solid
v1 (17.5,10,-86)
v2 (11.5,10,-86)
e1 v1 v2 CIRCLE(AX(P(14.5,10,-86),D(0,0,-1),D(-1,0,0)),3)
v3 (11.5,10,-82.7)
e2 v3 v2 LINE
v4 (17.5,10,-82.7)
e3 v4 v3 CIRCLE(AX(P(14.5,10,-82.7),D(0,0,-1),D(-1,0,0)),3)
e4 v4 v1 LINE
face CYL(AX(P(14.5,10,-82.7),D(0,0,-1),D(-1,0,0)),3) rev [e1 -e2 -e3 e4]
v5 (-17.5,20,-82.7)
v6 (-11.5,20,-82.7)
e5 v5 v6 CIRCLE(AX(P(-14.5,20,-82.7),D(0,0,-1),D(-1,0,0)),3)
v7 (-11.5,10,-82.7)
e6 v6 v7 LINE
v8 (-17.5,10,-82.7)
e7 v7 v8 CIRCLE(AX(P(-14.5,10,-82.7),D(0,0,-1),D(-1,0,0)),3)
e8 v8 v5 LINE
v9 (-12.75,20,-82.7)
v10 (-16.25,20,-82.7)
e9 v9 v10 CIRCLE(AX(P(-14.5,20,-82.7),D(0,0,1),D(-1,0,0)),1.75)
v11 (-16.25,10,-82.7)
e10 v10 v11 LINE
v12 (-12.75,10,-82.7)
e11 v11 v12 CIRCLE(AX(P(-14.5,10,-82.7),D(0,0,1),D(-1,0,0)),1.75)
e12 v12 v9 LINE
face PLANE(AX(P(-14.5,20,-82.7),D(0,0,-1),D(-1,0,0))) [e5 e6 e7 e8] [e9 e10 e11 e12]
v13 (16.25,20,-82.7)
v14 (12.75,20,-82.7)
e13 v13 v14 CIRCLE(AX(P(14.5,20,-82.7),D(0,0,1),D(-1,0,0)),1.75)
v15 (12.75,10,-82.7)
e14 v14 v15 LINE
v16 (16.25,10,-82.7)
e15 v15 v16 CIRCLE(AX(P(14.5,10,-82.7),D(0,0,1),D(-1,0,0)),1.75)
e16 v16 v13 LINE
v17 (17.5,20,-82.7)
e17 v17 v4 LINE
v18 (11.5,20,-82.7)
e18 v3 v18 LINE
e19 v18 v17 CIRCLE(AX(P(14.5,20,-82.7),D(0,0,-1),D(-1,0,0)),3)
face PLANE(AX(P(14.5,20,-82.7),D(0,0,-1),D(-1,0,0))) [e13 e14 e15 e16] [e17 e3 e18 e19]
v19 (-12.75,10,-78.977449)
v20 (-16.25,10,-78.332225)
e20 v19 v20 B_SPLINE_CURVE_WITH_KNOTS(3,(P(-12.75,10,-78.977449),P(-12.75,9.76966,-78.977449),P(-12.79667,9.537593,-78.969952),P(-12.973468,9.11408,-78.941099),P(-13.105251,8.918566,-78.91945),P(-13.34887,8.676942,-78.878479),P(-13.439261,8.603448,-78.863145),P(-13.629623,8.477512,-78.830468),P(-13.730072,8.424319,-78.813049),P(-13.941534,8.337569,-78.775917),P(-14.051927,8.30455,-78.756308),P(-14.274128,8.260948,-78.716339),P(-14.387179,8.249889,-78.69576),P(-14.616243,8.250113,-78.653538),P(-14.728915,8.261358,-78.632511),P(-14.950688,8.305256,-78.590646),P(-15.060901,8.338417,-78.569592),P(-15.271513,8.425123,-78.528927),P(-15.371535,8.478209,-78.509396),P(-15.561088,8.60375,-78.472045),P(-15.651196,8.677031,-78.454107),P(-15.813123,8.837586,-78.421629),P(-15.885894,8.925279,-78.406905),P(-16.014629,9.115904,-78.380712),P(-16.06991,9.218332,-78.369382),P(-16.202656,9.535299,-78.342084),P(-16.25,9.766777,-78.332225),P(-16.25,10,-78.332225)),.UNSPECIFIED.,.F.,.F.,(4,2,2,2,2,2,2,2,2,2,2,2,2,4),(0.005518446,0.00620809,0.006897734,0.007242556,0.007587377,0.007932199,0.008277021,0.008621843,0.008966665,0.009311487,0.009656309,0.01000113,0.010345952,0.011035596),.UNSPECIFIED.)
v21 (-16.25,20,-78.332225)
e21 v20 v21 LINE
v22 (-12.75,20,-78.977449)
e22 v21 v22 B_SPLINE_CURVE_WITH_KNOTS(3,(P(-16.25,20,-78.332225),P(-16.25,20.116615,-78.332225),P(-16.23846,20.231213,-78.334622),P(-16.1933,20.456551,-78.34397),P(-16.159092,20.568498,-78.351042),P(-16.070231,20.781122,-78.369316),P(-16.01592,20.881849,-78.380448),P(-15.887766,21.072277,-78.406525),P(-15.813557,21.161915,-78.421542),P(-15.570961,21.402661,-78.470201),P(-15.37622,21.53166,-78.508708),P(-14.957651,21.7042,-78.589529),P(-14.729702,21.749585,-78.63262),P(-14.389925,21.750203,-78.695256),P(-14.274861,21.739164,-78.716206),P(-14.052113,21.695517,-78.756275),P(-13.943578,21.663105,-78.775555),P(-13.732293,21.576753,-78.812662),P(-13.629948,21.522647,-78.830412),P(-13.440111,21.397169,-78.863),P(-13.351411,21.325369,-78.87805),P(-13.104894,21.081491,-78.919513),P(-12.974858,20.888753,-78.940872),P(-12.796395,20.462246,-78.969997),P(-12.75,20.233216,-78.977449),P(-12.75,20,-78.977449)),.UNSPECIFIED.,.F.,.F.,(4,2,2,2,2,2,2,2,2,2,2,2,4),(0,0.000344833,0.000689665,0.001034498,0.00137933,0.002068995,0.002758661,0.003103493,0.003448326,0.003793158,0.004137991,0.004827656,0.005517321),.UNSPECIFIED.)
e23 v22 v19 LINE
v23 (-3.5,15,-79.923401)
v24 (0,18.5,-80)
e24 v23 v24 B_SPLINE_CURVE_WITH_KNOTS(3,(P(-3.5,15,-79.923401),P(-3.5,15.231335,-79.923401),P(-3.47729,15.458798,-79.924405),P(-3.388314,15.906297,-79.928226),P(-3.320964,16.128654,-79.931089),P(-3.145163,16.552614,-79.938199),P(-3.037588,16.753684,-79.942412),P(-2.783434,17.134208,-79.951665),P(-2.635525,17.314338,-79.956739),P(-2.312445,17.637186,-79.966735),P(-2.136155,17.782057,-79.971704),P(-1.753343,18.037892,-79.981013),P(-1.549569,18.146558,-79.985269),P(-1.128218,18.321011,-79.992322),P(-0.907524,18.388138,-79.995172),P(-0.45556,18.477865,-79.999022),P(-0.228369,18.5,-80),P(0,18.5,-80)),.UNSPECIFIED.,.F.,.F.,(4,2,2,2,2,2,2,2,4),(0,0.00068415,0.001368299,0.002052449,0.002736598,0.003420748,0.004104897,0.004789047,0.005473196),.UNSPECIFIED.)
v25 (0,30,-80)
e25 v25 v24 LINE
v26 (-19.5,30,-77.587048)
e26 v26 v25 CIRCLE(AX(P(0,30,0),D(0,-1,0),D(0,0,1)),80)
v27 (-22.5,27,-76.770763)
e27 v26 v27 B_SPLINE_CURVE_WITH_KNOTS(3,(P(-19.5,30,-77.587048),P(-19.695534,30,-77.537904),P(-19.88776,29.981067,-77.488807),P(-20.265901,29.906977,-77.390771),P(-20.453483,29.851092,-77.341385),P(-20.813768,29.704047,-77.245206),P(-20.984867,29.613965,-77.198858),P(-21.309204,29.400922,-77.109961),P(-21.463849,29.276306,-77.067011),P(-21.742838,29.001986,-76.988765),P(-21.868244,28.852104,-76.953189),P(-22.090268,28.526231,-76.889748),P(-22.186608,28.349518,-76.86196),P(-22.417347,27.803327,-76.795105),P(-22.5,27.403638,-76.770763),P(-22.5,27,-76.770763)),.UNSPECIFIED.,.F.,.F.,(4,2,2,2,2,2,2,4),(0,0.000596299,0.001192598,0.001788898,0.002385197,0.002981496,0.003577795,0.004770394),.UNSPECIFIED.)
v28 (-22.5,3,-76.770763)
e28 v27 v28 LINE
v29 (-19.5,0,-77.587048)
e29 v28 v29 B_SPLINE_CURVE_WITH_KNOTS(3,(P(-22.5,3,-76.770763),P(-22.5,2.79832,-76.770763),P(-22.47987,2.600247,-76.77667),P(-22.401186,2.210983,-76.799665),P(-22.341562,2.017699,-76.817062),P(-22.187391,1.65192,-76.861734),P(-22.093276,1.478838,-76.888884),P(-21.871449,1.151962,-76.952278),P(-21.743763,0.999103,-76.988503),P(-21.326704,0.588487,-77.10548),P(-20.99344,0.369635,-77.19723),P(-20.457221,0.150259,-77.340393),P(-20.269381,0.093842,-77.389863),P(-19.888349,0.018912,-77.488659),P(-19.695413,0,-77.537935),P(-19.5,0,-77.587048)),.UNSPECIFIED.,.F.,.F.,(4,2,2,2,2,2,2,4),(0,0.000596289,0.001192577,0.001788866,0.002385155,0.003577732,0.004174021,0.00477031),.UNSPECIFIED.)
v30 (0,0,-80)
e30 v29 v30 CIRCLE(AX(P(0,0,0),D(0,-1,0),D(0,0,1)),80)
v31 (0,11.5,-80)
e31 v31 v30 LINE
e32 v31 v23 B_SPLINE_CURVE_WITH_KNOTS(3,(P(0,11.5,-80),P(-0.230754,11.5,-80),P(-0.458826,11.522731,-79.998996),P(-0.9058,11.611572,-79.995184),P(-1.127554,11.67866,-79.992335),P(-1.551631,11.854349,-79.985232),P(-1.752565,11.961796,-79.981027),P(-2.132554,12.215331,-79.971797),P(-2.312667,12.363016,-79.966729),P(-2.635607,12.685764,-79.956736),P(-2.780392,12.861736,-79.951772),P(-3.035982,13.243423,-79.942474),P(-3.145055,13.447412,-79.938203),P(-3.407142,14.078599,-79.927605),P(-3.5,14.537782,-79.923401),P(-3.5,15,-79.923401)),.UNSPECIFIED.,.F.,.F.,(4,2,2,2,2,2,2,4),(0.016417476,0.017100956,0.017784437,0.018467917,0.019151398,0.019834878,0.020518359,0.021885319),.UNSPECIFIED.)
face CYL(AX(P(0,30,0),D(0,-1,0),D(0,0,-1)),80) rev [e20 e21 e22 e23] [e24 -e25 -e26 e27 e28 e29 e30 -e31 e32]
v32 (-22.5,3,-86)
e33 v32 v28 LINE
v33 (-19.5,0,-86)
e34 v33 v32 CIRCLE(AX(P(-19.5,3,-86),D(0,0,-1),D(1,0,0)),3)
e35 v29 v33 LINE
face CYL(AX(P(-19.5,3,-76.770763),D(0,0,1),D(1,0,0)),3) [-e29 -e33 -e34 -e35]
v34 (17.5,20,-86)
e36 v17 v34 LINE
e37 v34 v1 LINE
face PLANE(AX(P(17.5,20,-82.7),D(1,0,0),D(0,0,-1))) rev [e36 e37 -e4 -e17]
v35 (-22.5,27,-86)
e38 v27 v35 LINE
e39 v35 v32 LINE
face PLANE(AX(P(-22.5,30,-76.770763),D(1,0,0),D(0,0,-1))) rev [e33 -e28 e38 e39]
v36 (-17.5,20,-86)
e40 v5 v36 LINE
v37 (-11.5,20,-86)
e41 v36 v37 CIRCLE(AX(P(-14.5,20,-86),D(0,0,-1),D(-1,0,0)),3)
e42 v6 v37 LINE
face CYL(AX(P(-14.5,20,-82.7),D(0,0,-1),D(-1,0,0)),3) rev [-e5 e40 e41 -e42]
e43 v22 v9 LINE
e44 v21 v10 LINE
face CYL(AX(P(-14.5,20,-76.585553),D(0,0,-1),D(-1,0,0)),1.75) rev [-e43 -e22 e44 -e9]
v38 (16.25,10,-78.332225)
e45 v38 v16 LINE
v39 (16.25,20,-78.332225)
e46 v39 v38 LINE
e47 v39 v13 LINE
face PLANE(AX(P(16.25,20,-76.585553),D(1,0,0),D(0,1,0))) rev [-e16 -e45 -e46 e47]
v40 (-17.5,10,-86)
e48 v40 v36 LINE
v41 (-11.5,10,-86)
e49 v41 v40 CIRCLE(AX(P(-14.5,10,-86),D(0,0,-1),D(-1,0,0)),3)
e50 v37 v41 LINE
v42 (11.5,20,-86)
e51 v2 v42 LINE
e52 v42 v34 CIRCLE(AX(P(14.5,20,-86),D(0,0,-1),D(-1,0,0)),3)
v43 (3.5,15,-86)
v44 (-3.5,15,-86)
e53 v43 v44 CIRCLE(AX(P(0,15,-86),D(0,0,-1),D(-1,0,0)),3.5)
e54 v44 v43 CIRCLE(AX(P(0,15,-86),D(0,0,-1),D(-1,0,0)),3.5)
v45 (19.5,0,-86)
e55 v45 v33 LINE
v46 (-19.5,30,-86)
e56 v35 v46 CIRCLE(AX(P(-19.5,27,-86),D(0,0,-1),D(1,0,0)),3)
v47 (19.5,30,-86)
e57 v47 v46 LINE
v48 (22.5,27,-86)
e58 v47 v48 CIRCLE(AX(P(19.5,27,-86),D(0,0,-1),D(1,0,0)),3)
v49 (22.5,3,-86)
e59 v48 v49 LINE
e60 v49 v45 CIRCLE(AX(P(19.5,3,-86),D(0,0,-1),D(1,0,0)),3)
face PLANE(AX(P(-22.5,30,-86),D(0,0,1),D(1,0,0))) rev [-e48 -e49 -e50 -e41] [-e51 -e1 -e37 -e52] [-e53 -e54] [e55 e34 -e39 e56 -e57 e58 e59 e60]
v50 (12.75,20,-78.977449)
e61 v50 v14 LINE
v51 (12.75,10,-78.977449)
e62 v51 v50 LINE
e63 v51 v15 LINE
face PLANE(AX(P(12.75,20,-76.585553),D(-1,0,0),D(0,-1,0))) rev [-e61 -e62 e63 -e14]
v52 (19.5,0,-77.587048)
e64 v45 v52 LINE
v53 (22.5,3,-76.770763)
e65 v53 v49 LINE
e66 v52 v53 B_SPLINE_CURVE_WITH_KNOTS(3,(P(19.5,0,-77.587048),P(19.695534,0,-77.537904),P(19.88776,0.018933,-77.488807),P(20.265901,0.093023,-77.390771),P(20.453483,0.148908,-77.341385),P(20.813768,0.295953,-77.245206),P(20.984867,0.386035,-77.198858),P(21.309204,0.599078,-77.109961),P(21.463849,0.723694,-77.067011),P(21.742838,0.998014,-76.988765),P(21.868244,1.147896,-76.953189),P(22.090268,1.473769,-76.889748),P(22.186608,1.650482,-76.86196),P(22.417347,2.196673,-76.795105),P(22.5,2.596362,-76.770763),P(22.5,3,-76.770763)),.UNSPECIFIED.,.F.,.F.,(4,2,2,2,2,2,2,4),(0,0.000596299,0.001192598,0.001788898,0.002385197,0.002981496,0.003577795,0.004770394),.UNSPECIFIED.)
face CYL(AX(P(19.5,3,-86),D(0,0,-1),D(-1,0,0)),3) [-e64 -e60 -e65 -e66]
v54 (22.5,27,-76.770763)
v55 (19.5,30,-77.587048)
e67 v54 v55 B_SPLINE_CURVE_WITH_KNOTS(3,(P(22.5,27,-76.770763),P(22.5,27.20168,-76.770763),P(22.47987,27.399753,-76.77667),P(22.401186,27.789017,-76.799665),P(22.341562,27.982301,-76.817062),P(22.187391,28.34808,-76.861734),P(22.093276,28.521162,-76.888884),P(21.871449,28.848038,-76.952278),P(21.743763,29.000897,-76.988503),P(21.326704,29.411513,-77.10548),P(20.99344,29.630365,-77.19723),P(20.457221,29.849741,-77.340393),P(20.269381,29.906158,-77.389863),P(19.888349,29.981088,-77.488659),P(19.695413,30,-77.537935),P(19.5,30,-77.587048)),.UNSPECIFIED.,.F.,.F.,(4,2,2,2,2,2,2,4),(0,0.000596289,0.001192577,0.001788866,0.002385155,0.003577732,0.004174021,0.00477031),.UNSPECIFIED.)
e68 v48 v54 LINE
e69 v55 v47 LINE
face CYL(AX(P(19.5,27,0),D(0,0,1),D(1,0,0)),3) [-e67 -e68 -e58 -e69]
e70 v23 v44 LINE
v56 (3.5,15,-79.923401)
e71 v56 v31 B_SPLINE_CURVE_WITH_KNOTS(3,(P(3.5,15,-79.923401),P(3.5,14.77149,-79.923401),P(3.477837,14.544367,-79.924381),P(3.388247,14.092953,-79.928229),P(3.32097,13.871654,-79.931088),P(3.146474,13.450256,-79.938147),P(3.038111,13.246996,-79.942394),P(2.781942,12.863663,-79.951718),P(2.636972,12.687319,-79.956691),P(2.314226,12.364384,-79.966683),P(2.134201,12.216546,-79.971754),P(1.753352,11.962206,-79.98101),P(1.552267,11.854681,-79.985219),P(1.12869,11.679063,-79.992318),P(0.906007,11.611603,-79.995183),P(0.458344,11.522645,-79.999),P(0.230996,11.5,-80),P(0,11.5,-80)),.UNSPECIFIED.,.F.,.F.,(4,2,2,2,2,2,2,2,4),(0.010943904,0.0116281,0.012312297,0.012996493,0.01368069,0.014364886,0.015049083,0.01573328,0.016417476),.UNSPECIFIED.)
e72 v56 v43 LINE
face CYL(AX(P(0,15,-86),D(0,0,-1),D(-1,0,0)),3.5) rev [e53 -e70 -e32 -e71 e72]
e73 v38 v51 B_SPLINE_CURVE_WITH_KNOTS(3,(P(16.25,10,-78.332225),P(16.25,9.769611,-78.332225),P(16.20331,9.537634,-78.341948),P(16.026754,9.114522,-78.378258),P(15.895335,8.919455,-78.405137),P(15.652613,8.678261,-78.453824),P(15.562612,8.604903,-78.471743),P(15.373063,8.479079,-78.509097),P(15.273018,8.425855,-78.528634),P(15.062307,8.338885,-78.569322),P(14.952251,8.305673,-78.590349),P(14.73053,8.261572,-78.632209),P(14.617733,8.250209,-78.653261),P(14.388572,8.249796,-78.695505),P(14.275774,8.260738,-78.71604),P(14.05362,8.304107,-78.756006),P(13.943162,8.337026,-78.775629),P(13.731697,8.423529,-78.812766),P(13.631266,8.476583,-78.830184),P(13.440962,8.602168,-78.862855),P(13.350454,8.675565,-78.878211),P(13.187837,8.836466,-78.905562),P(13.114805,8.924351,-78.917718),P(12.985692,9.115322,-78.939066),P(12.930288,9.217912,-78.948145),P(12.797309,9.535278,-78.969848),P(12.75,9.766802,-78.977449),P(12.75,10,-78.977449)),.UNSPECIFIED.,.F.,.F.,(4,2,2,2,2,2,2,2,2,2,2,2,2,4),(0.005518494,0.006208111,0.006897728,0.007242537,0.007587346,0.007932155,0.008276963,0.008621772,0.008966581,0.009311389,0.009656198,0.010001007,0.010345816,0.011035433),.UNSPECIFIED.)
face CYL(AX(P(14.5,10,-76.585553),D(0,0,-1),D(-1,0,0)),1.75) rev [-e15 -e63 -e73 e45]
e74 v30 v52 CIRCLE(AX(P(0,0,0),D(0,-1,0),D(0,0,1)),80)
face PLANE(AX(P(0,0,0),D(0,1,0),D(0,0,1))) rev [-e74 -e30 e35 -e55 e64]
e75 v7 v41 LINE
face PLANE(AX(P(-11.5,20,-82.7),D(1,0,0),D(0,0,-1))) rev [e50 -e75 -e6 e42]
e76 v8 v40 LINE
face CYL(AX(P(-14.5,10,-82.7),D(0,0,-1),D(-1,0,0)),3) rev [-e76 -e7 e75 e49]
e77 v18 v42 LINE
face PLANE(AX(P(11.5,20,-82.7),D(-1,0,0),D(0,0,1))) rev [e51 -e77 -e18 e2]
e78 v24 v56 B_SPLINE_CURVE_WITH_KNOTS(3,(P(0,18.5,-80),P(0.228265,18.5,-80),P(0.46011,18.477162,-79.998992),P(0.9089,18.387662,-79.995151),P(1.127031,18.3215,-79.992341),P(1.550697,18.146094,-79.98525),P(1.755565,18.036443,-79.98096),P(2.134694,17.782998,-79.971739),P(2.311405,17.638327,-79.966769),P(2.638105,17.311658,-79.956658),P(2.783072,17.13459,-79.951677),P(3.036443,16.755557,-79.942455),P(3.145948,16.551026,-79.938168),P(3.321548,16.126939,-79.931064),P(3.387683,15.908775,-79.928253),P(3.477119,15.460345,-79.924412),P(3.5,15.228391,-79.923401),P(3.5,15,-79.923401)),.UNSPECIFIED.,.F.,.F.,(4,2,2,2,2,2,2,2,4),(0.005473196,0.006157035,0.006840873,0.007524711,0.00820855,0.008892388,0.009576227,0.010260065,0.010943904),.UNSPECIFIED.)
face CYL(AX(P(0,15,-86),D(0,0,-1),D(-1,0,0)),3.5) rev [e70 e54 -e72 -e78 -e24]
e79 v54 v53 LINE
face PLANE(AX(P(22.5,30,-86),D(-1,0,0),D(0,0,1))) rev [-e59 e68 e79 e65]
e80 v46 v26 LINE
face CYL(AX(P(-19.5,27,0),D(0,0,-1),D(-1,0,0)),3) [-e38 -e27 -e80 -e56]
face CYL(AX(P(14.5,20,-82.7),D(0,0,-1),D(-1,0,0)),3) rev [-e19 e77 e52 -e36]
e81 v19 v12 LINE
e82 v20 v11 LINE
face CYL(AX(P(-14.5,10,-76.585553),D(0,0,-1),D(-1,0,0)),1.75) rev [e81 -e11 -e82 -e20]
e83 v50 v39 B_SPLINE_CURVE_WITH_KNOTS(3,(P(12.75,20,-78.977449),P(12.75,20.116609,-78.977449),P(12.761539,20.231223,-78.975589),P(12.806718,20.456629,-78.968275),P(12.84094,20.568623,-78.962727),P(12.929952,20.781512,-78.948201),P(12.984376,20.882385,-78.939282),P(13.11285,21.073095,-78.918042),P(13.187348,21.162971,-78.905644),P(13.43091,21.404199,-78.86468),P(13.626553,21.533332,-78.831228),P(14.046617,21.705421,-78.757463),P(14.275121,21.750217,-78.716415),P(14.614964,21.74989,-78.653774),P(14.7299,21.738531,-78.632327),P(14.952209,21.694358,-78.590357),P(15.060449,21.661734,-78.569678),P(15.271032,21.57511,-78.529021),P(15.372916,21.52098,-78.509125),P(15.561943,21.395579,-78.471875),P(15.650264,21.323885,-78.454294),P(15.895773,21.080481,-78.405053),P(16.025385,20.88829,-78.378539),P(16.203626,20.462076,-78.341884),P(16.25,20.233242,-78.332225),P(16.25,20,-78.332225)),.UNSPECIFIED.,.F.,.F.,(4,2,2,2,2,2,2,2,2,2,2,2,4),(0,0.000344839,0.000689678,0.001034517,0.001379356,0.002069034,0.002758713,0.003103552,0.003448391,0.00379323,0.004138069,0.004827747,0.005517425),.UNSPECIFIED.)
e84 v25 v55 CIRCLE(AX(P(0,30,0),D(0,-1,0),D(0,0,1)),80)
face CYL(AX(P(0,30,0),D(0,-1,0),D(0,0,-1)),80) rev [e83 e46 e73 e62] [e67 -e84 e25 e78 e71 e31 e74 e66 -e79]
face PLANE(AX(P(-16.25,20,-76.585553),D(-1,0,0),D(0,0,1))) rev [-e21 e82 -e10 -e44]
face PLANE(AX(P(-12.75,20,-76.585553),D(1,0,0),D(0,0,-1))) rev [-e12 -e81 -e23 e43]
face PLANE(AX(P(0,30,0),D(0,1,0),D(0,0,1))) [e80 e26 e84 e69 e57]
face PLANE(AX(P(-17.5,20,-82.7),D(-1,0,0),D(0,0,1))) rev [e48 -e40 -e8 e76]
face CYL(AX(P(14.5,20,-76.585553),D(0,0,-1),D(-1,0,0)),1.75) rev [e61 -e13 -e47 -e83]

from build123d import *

# Parameters (mm, degrees)
BOSS_EXTRUDE1_DEPTH   = 30
FILLET1_R             = 3
M8X1_0_TAPPED_HOLE1_D = 7
CUT_EXTRUDE1_DEPTH    = 39.619021662
CUT_EXTRUDE2_DEPTH    = 3.3


with BuildPart() as part:
    # Sketch1 → Boss-Extrude1 (new body)
    with BuildSketch(Plane(origin=(0, 0, 0), x_dir=(1, 0, 0), z_dir=(0, 1, 0))):
        with BuildLine():
            Line((-22.5, 76.770762664), (-22.5, 86))
            Line((-22.5, 86), (22.5, 86))
            Line((22.5, 86), (22.5, 76.770762664))
            ThreePointArc((22.5, 76.770762664), (0, 80), (-22.5, 76.770762664))
        make_face()
    extrude(amount=BOSS_EXTRUDE1_DEPTH)

    # Fillet1
    fillet1_edges = [part.edges().sort_by_distance(p)[0] for p in [
        (22.5, 30, -81.385381332),
        (22.5, 0, -81.385381332),
        (-22.5, 0, -81.385381332),
        (-22.5, 30, -81.385381332),
    ]]
    fillet(fillet1_edges, radius=FILLET1_R)

    # M8x1.0 Tapped Hole1 (through all)
    with Locations(Plane(origin=(0, 0, -86), x_dir=(-1, 0, 0), z_dir=(0, 0, -1))):
        with Locations((0, 15)):
            Hole(M8X1_0_TAPPED_HOLE1_D / 2)

    # Sketch4 → Cut-Extrude1 (cut, through all)
    with BuildSketch(Plane(origin=(0, 0, -86), x_dir=(-1, 0, 0), z_dir=(0, 0, -1))):
        with BuildLine():
            Line((-12.75, 20), (-12.75, 10))
            ThreePointArc((-12.75, 10), (-14.5, 8.25), (-16.25, 10))
            Line((-16.25, 10), (-16.25, 20))
            ThreePointArc((-16.25, 20), (-14.5, 21.75), (-12.75, 20))
        make_face()
        with BuildLine():
            Line((16.25, 20), (16.25, 10))
            ThreePointArc((16.25, 10), (14.5, 8.25), (12.75, 10))
            Line((12.75, 10), (12.75, 20))
            ThreePointArc((12.75, 20), (14.5, 21.75), (16.25, 20))
        make_face()
    extrude(amount=-CUT_EXTRUDE1_DEPTH, mode=Mode.SUBTRACT)

    # Sketch5 → Cut-Extrude2 (cut)
    with BuildSketch(Plane(origin=(0, 0, -86), x_dir=(-1, 0, 0), z_dir=(0, 0, -1))):
        with BuildLine():
            Line((-11.5, 20), (-11.5, 10))
            ThreePointArc((-11.5, 10), (-14.5, 7), (-17.5, 10))
            Line((-17.5, 10), (-17.5, 20))
            ThreePointArc((-17.5, 20), (-14.5, 23), (-11.5, 20))
        make_face()
        with BuildLine():
            Line((17.5, 20), (17.5, 10))
            ThreePointArc((17.5, 10), (14.5, 7), (11.5, 10))
            Line((11.5, 10), (11.5, 20))
            ThreePointArc((11.5, 20), (14.5, 23), (17.5, 20))
        make_face()
    extrude(amount=-CUT_EXTRUDE2_DEPTH, mode=Mode.SUBTRACT)


solid = part.part
